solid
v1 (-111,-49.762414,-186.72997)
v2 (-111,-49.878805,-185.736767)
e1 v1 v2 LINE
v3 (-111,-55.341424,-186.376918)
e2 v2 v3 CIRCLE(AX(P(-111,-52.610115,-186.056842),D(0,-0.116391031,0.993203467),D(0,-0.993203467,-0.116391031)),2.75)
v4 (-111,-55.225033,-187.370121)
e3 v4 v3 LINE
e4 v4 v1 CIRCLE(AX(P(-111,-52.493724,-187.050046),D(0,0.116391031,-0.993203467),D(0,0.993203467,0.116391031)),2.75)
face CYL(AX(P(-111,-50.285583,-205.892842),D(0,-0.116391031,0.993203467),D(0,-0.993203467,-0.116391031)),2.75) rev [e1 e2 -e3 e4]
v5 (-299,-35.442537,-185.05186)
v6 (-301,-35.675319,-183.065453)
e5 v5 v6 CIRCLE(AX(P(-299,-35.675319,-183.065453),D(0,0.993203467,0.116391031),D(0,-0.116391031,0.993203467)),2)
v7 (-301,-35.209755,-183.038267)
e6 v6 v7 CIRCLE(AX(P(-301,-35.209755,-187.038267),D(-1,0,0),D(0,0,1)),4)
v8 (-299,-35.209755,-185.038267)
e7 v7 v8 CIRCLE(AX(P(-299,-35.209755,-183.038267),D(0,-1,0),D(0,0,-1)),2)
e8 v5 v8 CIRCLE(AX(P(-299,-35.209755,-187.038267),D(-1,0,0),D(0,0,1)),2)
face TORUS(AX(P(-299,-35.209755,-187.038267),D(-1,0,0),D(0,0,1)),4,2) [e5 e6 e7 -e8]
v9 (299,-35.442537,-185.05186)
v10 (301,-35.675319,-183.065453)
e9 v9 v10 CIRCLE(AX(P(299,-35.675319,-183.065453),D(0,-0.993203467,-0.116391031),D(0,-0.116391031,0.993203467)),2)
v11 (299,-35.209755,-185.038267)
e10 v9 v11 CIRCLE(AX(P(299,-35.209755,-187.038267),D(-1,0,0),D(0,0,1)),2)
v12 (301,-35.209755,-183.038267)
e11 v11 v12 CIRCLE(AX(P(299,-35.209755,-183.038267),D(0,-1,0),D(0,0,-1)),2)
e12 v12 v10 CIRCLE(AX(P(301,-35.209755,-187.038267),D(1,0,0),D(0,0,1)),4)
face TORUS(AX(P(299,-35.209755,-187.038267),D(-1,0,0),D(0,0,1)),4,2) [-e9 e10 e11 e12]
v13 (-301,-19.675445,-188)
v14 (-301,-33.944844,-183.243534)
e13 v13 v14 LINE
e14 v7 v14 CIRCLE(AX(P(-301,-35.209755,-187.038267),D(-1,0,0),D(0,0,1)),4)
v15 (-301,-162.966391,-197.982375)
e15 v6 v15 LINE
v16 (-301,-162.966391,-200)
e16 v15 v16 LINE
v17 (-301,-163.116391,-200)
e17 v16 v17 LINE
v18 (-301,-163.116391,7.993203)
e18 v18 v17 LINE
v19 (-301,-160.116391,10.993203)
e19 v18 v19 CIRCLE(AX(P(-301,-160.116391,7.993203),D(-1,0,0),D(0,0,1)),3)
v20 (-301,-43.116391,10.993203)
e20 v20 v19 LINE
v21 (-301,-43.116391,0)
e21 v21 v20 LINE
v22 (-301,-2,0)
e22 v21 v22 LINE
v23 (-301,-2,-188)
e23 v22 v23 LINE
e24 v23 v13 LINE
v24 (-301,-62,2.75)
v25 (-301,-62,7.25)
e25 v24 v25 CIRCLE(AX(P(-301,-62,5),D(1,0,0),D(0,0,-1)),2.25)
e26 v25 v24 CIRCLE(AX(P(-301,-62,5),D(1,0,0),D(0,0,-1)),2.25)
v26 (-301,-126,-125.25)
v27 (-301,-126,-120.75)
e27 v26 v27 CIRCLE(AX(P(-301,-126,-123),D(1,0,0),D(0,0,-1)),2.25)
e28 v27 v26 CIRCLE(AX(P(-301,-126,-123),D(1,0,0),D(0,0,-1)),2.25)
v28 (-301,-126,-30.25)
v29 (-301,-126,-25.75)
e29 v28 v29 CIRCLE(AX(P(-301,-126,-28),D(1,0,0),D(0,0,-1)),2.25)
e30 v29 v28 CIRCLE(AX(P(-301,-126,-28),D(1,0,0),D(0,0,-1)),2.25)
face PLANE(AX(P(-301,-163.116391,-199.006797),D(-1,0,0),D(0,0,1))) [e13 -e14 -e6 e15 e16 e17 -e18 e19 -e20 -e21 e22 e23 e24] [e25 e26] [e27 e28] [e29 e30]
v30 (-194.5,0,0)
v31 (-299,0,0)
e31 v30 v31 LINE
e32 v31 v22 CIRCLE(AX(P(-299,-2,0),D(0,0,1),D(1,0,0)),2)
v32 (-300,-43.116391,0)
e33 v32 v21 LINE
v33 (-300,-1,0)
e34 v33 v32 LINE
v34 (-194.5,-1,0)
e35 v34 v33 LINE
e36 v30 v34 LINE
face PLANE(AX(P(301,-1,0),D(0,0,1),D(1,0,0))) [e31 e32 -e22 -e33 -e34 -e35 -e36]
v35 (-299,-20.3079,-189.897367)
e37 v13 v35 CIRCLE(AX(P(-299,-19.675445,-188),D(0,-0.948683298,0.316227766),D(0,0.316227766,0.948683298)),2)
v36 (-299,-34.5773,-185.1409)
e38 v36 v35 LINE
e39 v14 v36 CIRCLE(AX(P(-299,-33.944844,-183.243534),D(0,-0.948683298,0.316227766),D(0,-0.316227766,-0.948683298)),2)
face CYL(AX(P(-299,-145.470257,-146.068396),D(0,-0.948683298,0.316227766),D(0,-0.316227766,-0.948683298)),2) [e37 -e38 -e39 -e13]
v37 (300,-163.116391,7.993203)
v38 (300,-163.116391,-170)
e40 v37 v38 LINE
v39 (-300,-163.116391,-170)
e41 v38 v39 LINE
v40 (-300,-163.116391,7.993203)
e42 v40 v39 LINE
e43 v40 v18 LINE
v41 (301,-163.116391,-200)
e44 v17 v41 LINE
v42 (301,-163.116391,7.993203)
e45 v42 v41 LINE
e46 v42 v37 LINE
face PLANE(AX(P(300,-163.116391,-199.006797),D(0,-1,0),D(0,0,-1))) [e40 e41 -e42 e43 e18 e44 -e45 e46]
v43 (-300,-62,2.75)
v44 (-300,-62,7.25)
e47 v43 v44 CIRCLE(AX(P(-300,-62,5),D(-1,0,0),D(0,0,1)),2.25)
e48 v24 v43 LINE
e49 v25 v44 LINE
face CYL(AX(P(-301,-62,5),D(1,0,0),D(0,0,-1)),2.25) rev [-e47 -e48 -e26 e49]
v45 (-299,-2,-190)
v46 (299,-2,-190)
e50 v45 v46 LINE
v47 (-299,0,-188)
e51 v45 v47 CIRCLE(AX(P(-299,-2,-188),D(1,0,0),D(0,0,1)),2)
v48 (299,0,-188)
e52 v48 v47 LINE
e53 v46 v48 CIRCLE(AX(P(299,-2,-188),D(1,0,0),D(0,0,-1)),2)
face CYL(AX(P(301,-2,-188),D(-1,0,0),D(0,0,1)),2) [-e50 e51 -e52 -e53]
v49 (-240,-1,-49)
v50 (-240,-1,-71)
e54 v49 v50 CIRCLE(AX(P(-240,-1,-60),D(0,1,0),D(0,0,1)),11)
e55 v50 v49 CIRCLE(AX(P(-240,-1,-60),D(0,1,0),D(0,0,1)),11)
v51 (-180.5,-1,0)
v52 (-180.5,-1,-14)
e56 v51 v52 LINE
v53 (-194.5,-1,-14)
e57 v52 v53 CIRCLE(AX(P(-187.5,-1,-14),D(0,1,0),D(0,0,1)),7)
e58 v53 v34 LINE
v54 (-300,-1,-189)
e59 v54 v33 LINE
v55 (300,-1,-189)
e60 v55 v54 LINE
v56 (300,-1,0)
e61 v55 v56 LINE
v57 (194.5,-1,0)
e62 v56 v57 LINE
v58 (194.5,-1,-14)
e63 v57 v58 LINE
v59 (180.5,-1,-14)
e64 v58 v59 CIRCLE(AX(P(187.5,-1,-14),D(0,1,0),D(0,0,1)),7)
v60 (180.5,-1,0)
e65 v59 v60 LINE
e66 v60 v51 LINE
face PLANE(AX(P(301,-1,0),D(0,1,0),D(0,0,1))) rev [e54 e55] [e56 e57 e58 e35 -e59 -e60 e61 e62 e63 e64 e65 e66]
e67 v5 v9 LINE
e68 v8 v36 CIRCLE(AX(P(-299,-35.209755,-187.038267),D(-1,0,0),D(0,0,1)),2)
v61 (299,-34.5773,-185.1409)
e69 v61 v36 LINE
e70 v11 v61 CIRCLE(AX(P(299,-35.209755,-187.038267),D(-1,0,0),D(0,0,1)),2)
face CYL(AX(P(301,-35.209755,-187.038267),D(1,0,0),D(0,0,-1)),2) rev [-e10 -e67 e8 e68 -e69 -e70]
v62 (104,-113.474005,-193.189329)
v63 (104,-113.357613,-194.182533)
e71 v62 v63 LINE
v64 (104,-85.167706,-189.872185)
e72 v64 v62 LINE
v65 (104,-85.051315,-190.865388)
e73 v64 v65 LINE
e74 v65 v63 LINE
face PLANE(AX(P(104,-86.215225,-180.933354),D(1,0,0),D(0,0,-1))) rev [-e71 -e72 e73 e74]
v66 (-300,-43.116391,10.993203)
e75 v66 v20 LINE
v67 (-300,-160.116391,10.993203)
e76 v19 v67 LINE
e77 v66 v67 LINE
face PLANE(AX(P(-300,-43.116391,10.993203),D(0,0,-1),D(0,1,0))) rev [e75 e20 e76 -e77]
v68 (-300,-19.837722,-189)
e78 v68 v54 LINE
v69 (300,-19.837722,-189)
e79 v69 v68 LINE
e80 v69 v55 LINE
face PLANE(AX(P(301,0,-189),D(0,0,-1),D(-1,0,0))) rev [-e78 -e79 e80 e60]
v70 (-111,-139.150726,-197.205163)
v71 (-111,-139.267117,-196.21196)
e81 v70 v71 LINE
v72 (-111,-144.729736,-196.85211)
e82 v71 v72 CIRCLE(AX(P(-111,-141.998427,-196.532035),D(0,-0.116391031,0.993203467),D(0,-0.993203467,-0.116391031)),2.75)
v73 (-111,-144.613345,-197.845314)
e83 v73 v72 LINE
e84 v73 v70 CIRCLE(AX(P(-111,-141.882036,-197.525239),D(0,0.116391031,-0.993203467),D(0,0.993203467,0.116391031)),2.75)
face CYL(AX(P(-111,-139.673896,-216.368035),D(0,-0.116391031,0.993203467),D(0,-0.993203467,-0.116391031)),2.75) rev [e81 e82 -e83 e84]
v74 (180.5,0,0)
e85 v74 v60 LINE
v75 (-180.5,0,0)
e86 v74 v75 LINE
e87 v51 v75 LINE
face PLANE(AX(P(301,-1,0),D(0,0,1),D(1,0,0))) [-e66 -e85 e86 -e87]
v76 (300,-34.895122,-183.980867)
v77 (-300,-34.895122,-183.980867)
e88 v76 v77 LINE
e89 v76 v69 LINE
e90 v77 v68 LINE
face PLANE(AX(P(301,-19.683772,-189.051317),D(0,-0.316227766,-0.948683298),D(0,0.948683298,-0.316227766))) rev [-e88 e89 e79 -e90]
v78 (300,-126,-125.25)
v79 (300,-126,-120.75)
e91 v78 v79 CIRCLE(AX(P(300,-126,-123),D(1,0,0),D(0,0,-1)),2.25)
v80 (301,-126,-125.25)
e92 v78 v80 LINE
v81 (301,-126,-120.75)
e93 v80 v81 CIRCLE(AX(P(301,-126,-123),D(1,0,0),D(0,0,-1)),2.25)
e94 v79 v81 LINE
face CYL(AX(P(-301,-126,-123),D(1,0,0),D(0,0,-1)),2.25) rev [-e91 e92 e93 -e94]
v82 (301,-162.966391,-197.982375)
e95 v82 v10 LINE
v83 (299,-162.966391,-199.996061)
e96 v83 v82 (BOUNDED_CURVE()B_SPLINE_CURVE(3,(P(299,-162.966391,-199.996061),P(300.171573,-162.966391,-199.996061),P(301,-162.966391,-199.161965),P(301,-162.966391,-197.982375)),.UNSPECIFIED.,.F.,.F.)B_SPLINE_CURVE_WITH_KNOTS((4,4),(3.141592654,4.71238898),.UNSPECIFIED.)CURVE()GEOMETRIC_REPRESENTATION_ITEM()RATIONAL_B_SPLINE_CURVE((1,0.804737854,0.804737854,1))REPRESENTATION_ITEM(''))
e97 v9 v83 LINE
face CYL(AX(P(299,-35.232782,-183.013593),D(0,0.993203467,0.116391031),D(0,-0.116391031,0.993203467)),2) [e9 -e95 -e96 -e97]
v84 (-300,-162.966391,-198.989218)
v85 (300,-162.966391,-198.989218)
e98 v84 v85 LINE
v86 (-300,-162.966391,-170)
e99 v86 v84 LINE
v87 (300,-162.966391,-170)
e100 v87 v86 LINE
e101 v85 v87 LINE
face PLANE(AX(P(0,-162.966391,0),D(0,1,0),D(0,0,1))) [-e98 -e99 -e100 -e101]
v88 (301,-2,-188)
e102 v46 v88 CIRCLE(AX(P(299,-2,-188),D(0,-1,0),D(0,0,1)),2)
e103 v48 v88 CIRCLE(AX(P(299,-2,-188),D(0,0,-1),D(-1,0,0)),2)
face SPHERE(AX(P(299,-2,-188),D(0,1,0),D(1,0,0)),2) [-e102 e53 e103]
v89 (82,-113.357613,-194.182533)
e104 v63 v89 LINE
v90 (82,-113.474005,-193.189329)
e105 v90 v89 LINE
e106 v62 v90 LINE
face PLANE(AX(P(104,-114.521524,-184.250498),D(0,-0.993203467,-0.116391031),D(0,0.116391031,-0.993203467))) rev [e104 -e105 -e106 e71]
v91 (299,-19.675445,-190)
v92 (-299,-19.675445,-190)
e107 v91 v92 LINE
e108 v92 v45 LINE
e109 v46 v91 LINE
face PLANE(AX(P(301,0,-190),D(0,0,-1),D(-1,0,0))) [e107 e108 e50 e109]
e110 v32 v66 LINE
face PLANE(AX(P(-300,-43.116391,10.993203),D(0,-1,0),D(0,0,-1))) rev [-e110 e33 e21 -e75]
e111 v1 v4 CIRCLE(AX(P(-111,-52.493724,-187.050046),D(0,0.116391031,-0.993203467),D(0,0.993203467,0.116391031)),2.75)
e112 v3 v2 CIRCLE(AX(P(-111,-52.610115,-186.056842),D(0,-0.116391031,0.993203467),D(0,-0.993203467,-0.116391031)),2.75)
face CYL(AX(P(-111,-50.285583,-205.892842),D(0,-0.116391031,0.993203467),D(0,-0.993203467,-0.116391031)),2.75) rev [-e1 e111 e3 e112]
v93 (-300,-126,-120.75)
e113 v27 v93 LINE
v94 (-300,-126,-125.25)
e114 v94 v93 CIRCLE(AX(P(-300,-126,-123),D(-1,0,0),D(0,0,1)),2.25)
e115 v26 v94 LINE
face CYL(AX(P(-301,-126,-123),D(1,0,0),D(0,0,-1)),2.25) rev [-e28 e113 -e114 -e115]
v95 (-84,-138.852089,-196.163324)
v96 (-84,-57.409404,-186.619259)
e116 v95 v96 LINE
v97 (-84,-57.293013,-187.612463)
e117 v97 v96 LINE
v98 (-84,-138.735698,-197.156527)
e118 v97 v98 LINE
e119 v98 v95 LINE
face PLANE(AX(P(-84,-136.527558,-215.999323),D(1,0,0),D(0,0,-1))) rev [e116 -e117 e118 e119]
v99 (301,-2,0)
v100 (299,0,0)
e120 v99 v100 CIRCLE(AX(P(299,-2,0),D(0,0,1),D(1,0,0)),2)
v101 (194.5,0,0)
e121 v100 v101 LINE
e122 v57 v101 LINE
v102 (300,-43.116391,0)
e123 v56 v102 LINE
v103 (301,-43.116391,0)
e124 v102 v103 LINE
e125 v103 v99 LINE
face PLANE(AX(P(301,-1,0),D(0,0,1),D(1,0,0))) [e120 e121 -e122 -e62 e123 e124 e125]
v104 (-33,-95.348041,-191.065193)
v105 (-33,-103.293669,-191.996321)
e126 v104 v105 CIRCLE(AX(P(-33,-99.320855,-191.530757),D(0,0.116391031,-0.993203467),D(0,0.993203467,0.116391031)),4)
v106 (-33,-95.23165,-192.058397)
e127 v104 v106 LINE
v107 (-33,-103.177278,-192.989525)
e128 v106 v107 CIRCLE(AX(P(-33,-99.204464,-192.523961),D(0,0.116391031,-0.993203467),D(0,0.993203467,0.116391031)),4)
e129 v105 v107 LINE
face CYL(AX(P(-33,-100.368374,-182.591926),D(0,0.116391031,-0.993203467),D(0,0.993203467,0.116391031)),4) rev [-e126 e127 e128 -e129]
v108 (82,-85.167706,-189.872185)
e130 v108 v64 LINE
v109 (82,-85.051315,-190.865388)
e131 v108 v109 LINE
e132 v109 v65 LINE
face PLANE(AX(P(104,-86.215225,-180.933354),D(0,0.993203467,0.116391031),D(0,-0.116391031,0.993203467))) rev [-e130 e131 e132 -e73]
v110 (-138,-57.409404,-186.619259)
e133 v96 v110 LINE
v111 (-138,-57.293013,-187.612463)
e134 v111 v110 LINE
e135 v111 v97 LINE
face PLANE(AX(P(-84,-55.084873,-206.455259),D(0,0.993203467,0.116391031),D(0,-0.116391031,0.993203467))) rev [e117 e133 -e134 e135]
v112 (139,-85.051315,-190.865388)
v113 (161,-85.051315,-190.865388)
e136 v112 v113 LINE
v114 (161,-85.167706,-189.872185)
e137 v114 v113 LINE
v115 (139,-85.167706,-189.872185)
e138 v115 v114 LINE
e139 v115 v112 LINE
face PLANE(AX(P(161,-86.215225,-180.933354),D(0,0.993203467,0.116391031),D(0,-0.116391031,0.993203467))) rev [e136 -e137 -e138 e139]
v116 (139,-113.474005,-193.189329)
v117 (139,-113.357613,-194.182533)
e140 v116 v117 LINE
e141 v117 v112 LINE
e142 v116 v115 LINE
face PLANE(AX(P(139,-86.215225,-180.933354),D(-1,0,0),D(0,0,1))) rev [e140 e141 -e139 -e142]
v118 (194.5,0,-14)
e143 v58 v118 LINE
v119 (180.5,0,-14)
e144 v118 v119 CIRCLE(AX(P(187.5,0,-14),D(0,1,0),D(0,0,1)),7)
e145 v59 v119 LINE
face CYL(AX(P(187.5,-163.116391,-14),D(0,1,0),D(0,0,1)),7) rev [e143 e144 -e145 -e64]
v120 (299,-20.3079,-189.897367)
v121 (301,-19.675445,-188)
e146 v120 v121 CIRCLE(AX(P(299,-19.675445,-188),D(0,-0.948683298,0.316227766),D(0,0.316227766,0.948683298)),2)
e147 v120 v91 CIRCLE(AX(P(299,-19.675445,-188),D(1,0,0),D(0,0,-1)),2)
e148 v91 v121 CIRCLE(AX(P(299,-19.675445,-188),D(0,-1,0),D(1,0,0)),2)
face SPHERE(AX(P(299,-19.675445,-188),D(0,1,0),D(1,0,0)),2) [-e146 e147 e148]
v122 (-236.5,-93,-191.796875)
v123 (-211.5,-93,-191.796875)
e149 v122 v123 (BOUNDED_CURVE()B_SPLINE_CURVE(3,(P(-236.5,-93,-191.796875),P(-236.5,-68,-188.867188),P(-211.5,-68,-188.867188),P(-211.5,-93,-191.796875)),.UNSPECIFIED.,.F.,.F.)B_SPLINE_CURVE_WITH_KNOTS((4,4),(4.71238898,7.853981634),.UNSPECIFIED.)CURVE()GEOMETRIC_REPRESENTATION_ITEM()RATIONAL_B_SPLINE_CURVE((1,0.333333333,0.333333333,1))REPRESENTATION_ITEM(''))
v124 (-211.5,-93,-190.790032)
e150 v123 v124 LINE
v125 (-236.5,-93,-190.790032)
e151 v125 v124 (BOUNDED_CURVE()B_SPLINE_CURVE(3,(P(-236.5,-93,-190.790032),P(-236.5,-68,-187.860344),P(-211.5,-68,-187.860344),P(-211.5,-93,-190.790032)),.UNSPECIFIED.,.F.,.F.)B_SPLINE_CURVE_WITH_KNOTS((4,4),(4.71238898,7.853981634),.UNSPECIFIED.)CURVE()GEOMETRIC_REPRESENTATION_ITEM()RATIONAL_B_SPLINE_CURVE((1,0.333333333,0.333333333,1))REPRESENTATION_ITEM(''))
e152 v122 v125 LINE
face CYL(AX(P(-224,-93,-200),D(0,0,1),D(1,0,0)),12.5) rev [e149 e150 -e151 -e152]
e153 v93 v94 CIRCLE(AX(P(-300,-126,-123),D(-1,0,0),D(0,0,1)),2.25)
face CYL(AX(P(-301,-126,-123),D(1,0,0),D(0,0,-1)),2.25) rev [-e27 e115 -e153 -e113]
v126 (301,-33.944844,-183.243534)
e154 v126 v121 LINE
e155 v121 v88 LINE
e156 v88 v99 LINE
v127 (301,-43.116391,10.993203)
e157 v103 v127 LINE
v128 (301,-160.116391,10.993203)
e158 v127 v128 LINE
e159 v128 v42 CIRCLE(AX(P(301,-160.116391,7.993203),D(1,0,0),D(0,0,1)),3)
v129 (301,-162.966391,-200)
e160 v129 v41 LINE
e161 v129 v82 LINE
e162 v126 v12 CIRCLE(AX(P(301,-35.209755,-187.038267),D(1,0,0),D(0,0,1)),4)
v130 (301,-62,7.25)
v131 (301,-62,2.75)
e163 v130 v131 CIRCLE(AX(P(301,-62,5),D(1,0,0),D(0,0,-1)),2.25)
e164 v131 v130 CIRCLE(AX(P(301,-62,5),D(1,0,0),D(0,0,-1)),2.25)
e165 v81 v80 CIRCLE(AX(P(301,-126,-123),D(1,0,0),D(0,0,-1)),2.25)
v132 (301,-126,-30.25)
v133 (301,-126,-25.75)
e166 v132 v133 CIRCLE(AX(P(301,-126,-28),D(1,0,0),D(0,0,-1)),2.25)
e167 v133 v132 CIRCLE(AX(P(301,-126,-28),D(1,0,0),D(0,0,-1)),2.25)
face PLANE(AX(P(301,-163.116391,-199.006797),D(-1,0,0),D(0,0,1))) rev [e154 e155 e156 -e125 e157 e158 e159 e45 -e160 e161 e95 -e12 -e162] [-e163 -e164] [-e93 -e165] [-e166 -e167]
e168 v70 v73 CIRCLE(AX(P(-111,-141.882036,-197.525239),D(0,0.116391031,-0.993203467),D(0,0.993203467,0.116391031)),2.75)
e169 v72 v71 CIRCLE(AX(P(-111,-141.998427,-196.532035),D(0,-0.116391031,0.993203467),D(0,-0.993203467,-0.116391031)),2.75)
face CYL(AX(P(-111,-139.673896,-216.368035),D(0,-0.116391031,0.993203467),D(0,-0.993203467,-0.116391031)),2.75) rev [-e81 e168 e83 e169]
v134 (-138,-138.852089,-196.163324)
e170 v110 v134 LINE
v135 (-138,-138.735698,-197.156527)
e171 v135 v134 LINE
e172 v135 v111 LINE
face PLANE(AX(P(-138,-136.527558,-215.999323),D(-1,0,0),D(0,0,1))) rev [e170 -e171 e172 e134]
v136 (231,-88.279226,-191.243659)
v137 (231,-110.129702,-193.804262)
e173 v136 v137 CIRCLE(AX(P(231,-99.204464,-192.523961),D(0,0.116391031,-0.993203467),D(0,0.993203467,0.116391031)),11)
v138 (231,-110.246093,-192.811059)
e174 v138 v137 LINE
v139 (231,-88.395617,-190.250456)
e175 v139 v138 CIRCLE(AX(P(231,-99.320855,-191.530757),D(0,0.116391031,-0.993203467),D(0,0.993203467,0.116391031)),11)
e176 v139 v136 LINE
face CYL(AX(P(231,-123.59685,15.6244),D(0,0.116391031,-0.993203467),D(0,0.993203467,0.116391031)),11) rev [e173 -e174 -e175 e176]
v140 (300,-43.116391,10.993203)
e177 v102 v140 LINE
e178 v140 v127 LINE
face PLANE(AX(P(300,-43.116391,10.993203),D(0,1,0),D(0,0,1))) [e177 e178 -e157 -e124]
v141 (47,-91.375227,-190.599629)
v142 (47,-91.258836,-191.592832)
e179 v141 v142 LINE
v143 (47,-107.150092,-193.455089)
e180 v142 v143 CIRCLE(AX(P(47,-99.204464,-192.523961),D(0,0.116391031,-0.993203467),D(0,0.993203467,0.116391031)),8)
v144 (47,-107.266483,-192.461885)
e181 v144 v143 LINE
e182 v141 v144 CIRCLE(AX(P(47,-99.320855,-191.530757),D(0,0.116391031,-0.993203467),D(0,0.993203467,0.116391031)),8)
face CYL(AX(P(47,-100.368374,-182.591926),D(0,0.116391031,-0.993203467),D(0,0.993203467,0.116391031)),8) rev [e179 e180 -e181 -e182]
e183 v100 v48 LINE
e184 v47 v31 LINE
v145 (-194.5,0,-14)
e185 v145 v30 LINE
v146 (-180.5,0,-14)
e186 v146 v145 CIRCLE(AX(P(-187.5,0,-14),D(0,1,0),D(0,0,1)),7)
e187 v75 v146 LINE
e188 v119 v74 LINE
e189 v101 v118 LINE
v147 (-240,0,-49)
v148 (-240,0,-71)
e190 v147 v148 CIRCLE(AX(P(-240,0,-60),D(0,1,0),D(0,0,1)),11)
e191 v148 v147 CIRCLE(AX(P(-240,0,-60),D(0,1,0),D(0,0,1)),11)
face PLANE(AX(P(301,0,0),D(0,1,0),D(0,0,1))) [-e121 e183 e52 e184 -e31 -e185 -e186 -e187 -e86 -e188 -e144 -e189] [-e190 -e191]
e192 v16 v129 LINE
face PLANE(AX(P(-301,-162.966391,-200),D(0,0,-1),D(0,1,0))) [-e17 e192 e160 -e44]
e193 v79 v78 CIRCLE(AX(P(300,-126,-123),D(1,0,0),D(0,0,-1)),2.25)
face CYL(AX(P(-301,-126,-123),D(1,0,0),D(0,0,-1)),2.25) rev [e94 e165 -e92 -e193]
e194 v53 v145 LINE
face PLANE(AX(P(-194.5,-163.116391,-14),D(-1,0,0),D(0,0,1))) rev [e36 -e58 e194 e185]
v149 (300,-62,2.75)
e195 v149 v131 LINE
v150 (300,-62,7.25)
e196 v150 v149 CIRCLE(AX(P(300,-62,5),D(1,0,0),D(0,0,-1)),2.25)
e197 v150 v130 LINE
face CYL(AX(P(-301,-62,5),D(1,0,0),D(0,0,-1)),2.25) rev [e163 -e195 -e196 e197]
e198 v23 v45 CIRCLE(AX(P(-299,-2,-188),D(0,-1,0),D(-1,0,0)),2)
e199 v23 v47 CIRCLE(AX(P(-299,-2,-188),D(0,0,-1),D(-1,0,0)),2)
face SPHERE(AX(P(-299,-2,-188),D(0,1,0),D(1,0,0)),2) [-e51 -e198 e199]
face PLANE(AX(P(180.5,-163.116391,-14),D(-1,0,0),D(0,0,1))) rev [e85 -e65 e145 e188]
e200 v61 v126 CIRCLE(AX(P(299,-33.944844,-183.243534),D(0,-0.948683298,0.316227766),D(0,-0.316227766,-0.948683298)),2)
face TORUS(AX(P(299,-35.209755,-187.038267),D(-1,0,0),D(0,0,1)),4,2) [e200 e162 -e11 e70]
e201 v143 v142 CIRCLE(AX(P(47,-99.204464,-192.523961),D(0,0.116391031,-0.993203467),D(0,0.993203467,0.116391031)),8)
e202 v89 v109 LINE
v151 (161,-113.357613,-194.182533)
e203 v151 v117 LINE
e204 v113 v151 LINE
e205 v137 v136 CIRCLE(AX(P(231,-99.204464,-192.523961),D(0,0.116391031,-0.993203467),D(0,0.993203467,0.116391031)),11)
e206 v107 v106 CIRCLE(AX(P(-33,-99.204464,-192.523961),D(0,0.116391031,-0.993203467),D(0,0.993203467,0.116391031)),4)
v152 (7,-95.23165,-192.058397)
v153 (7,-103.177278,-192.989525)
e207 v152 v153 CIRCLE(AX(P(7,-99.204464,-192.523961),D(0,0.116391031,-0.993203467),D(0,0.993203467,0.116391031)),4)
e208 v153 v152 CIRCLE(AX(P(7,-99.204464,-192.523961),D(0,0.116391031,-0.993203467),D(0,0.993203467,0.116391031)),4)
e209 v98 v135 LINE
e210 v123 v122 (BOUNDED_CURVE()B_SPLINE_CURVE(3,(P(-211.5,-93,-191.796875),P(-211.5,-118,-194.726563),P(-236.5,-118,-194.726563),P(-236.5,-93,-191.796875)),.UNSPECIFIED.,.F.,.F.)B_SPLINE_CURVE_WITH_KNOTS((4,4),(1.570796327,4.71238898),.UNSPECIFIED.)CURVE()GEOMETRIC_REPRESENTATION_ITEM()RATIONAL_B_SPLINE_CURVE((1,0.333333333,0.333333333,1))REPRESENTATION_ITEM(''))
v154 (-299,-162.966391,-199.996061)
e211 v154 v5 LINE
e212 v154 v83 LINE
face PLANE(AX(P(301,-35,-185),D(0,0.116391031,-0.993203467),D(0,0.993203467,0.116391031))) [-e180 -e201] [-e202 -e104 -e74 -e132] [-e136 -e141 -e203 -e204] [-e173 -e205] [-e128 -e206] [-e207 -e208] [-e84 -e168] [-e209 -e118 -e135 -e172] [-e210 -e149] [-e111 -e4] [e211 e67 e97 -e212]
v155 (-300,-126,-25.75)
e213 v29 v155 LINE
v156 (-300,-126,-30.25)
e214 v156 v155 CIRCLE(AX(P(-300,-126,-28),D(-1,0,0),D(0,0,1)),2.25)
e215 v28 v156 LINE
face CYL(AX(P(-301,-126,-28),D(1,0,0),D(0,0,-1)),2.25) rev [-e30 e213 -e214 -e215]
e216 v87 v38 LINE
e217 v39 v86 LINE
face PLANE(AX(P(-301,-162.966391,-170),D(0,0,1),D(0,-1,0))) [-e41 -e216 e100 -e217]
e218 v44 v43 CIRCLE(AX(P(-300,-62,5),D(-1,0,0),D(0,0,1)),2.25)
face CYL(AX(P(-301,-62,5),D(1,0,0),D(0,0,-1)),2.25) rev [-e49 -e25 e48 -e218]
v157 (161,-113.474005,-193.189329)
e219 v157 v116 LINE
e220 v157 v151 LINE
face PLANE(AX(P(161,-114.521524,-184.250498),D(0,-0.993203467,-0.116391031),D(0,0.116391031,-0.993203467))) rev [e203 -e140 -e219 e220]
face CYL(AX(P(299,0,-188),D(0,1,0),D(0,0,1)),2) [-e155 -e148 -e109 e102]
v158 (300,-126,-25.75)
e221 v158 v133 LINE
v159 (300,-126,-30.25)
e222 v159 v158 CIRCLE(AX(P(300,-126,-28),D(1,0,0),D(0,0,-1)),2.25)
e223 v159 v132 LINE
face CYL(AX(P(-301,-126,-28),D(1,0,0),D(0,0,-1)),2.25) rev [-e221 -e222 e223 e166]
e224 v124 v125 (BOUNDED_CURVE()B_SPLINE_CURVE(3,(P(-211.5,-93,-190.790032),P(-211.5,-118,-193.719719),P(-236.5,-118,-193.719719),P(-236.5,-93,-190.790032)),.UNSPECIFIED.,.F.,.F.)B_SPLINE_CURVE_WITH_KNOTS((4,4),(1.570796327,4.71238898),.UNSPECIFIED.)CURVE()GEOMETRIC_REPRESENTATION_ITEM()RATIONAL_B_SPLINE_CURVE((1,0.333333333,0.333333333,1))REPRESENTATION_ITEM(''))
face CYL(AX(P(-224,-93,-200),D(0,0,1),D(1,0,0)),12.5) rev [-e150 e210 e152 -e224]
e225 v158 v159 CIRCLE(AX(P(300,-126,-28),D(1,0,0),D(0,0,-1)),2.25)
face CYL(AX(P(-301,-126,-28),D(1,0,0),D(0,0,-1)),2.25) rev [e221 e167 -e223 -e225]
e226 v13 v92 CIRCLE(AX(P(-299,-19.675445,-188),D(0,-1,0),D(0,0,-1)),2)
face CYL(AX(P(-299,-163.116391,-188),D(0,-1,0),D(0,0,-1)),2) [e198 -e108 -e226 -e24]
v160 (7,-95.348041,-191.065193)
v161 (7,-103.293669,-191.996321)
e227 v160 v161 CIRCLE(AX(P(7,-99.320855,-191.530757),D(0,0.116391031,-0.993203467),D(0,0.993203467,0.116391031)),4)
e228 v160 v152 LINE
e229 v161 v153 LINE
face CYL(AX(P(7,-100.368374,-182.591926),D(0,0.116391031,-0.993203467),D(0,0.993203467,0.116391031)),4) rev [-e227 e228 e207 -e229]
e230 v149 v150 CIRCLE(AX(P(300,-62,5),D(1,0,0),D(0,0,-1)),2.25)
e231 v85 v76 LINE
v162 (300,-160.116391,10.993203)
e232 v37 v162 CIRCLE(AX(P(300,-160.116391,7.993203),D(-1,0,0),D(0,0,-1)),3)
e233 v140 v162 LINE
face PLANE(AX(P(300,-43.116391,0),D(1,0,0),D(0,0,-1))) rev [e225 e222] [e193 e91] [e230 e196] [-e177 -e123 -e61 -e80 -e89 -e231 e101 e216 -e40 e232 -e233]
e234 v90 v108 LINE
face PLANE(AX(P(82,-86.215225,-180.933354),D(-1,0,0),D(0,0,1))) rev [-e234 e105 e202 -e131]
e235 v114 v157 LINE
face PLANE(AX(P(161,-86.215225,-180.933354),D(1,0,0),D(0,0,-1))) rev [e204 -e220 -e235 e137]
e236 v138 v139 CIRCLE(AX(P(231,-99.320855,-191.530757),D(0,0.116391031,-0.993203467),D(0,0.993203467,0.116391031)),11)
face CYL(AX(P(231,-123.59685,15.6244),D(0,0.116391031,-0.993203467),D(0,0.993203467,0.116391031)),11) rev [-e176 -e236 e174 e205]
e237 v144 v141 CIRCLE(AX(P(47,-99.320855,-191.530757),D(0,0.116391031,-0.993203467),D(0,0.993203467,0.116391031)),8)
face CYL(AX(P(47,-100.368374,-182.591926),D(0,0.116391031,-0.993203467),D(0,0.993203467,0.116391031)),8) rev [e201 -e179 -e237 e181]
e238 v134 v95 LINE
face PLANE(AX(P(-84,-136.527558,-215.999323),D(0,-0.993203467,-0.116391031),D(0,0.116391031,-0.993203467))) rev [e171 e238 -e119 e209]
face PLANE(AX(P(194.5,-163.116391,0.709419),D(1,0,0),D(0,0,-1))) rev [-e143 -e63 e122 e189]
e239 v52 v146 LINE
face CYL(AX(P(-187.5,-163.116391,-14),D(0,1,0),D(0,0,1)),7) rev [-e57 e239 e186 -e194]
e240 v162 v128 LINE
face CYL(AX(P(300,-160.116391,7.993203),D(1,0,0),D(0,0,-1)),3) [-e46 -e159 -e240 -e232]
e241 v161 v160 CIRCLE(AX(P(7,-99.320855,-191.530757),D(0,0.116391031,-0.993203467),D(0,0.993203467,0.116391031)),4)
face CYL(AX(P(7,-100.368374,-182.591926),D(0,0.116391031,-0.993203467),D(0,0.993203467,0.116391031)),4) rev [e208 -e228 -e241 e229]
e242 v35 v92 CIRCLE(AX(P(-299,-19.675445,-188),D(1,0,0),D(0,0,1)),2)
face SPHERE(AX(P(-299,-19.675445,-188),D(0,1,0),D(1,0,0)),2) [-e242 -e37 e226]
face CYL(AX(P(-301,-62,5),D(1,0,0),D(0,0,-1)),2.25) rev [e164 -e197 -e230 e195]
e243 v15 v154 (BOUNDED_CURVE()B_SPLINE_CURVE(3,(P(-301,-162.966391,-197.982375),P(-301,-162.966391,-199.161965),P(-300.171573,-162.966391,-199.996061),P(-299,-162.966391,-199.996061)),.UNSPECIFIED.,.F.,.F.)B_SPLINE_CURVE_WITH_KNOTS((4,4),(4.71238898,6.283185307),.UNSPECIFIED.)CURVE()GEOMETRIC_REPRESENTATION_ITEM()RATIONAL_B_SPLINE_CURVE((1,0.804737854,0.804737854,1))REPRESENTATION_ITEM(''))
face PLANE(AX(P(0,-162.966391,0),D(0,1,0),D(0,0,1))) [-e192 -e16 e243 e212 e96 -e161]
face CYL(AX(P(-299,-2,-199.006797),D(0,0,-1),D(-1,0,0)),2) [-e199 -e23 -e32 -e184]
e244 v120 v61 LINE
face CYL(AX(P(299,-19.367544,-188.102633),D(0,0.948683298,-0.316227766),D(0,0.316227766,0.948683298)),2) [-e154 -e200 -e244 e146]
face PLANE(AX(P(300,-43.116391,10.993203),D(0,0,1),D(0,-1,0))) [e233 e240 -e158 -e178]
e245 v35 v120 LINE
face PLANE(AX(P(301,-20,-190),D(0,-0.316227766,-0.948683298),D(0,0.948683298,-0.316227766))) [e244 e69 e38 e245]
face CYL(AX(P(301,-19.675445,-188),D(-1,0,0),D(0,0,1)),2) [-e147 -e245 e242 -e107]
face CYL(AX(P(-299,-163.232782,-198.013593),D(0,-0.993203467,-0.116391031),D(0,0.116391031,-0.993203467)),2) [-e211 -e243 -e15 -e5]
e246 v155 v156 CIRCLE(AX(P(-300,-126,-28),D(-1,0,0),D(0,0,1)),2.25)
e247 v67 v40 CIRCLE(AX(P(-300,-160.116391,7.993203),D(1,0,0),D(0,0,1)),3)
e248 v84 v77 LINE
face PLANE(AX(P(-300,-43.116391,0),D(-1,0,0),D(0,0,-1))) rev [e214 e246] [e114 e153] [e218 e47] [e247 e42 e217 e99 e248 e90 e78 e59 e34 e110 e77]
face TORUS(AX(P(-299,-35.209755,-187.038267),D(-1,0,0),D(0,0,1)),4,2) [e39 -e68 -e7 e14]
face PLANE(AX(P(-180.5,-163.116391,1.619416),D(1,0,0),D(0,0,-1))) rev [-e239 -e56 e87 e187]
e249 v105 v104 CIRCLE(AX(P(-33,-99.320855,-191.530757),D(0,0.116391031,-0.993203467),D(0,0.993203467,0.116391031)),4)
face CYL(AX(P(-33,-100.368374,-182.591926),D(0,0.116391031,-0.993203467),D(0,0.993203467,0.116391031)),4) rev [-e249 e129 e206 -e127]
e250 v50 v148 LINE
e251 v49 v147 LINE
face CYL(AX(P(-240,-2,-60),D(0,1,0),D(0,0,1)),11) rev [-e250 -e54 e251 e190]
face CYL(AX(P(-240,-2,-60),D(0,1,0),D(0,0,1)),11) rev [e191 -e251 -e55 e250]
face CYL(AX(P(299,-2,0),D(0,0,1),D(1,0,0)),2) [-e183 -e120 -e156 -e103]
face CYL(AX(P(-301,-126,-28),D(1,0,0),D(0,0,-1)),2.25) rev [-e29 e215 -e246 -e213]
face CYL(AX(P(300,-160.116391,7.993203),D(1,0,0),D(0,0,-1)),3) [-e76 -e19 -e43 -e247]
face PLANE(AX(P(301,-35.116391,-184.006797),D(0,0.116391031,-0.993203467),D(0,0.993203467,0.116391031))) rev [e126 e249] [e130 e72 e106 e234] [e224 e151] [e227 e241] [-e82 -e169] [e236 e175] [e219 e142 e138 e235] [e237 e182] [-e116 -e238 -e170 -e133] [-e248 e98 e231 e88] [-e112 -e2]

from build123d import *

# Parameters (mm, degrees)
EXTRUDE_1_DEPTH      = 301
EXTRUDE_1_2_DEPTH    = 1
SKETCH_8_R           = 11
CUT_EXTRUDE_3_DEPTH  = 2
SKETCH_12_R          = 12.5
CUT_EXTRUDE_6_DEPTH  = 397.494586373
SKETCH_13_W          = 602
SKETCH_13_H          = 30
EXTRUDE_5_DEPTH      = 0.15
SKETCH_14_R          = 2.25
CUT_EXTRUDE_7_DEPTH  = 655.989280083
FILLET_1_R           = 2
CUT_EXTRUDE_8_DEPTH  = 397.494586373
SKETCH_16_R          = 2.75
SKETCH_16_W          = 54
SKETCH_16_H          = 82
CUT_EXTRUDE_9_DEPTH  = 400.921435854
SKETCH_17_R          = 4
SKETCH_17_R_2        = 8
SKETCH_17_W          = 22
SKETCH_17_H          = 28.5
CUT_EXTRUDE_11_DEPTH = 10
FILLET_2_R           = 3
FILLET_3_R           = 3
SKETCH_19_R          = 11
CUT_EXTRUDE_12_DEPTH = 401.443879104


with BuildPart() as part:
    # 草图2 → Extrude 1 (new, symmetric)
    with BuildSketch(Plane(origin=(0, 0, 0), x_dir=(0, 0, -1), z_dir=(1, 0, 0))):
        Polygon((0, 0), (190, 0), (190, -20), (185, -35), (200, -163), (199.006796533, -163.116391031), (183.980866623, -34.895122471), (189, -19.83772234), (189, -1), (0, -1), align=None)
    extrude(amount=EXTRUDE_1_DEPTH, both=True)

    # 草图5 → Extrude 1 2 (add)
    with BuildSketch(Plane(origin=(301, 0, 0), x_dir=(0, 0, -1), z_dir=(1, 0, 0))):
        Polygon((0, -1), (189, -1), (189, -19.83772234), (183.980866623, -34.895122471), (199.006796533, -163.116391031), (-0.993203467, -163.116391031), (-10.993203467, -163.116391031), (-10.993203467, -43.116391031), (0, -43.116391031), align=None)
    extrude_1_2 = extrude(amount=-EXTRUDE_1_2_DEPTH)

    # 镜向1: Extrude 1 2 across plane
    add(extrude_1_2.mirror(Plane(origin=(0, 0, 0), x_dir=(0, 0, 1), z_dir=(1, 0, 0))))

    # 草图8 → 切除-拉伸3 (cut)
    with BuildSketch(Plane(origin=(0, 0, 0), x_dir=(-1, 0, 0), z_dir=(0, 1, 0))):
        with Locations(Location((240, -60, 0), (0, 0, 90))):
            Circle(SKETCH_8_R)
    extrude(amount=-CUT_EXTRUDE_3_DEPTH, mode=Mode.SUBTRACT)

    # 草图12 → 切除-拉伸6 (cut, through all)
    with BuildSketch(Plane.XY):
        with Locations(Location((-224, -93, 0), (0, 0, 90))):
            Circle(SKETCH_12_R)
    extrude(amount=-CUT_EXTRUDE_6_DEPTH, mode=Mode.SUBTRACT)

    # 草图13 → 凸台-拉伸5 (add)
    with BuildSketch(Plane.XZ.offset(163.116391031)):
        with Locations((0, -185)):
            Rectangle(SKETCH_13_W, SKETCH_13_H)
    extrude(amount=-EXTRUDE_5_DEPTH)

    # 草图14 → 切除-拉伸7 (cut, through all)
    with BuildSketch(Plane(origin=(301, 0, 0), x_dir=(0, 0, -1), z_dir=(1, 0, 0))):
        with Locations((-5, -62)):
            Circle(SKETCH_14_R)
        with Locations((28, -126)):
            Circle(SKETCH_14_R)
        with Locations((123, -126)):
            Circle(SKETCH_14_R)
    extrude(amount=-CUT_EXTRUDE_7_DEPTH, mode=Mode.SUBTRACT)

    # 圆角1
    fillet_1_edges = [part.edges().sort_by_distance(p)[0] for p in [
        (301, -98.983195516, -192.498030724),
        (-301, -98.983195516, -192.498030724),
        (301, -27.5, -187.5),
        (0, 0, -190),
        (0, -20, -190),
        (0, -35, -185),
        (301, -10, -190),
        (301, 0, -95),
        (-301, 0, -95),
        (-301, -10, -190),
        (-301, -27.5, -187.5),
    ]]
    fillet(fillet_1_edges, radius=FILLET_1_R)

    # 草图15 → 切除-拉伸8 (cut, through all)
    with BuildSketch(Plane(origin=(0, 0, 0), x_dir=(1, 0, 0), z_dir=(0, 1, 0))):
        with BuildLine():
            Line((180.5, 14), (180.5, -0.70941875))
            Line((180.5, -0.70941875), (194.5, -0.70941875))
            Line((194.5, -0.70941875), (194.5, 14))
            ThreePointArc((194.5, 14), (187.5, 21), (180.5, 14))
        make_face()
        with BuildLine():
            Line((-194.5, 14), (-194.5, -1.619416497))
            Line((-194.5, -1.619416497), (-180.5, -1.619416497))
            Line((-180.5, -1.619416497), (-180.5, 14))
            ThreePointArc((-180.5, 14), (-187.5, 21), (-194.5, 14))
        make_face()
    extrude(amount=-CUT_EXTRUDE_8_DEPTH, mode=Mode.SUBTRACT)

    # 草图16 → 切除-拉伸9 (cut, through all)
    with BuildSketch(Plane(origin=(0, 20.795463987, -177.454626023), x_dir=(1, 0, 0), z_dir=(0, -0.11639103134578274, 0.9932034674840121))):
        with Locations(Location((-111, -163.907896051, 0), (0, 0, 270))):
            Circle(SKETCH_16_R)
        with Locations(Location((-111, -73.907896051, 0), (0, 0, 270))):
            Circle(SKETCH_16_R)
        with Locations((-111, -119.740027582)):
            Rectangle(SKETCH_16_W, SKETCH_16_H)
    extrude(amount=-CUT_EXTRUDE_9_DEPTH, mode=Mode.SUBTRACT)

    # 草图17 → 切除-拉伸11 (cut)
    with BuildSketch(Plane(origin=(0, 20.911855018, -178.44782949), x_dir=(-1, 0, 0), z_dir=(0, 0.11639103134578274, -0.9932034674840121))):
        with Locations(Location((-7, -120.938280048, 0), (0, 0, 90))):
            Circle(SKETCH_17_R)
        with Locations(Location((33, -120.938280048, 0), (0, 0, 90))):
            Circle(SKETCH_17_R)
        with Locations(Location((-47, -120.938280048, 0), (0, 0, 90))):
            Circle(SKETCH_17_R_2)
        with Locations((-150, -120.938280048)):
            Rectangle(SKETCH_17_W, SKETCH_17_H)
        with Locations((-93, -120.938280048)):
            Rectangle(SKETCH_17_W, SKETCH_17_H)
    extrude(amount=-CUT_EXTRUDE_11_DEPTH, mode=Mode.SUBTRACT)

    # 圆角2
    fillet_2_edges = [part.edges().sort_by_distance(p)[0] for p in [
        (-300.5, -163.116391031, 10.993203467),
    ]]
    fillet(fillet_2_edges, radius=FILLET_2_R)

    # 圆角3
    fillet_3_edges = [part.edges().sort_by_distance(p)[0] for p in [
        (300.5, -163.116391031, 10.993203467),
    ]]
    fillet(fillet_3_edges, radius=FILLET_3_R)

    # 草图19 → 切除-拉伸12 (cut, through all)
    with BuildSketch(Plane(origin=(0, 20.911855018, -178.44782949), x_dir=(-1, 0, 0), z_dir=(0, 0.11639103134578274, -0.993203467484012))):
        with Locations(Location((-231, -120.938280048, 0), (0, 0, 90))):
            Circle(SKETCH_19_R)
    extrude(amount=-CUT_EXTRUDE_12_DEPTH, mode=Mode.SUBTRACT)


solid = part.part
